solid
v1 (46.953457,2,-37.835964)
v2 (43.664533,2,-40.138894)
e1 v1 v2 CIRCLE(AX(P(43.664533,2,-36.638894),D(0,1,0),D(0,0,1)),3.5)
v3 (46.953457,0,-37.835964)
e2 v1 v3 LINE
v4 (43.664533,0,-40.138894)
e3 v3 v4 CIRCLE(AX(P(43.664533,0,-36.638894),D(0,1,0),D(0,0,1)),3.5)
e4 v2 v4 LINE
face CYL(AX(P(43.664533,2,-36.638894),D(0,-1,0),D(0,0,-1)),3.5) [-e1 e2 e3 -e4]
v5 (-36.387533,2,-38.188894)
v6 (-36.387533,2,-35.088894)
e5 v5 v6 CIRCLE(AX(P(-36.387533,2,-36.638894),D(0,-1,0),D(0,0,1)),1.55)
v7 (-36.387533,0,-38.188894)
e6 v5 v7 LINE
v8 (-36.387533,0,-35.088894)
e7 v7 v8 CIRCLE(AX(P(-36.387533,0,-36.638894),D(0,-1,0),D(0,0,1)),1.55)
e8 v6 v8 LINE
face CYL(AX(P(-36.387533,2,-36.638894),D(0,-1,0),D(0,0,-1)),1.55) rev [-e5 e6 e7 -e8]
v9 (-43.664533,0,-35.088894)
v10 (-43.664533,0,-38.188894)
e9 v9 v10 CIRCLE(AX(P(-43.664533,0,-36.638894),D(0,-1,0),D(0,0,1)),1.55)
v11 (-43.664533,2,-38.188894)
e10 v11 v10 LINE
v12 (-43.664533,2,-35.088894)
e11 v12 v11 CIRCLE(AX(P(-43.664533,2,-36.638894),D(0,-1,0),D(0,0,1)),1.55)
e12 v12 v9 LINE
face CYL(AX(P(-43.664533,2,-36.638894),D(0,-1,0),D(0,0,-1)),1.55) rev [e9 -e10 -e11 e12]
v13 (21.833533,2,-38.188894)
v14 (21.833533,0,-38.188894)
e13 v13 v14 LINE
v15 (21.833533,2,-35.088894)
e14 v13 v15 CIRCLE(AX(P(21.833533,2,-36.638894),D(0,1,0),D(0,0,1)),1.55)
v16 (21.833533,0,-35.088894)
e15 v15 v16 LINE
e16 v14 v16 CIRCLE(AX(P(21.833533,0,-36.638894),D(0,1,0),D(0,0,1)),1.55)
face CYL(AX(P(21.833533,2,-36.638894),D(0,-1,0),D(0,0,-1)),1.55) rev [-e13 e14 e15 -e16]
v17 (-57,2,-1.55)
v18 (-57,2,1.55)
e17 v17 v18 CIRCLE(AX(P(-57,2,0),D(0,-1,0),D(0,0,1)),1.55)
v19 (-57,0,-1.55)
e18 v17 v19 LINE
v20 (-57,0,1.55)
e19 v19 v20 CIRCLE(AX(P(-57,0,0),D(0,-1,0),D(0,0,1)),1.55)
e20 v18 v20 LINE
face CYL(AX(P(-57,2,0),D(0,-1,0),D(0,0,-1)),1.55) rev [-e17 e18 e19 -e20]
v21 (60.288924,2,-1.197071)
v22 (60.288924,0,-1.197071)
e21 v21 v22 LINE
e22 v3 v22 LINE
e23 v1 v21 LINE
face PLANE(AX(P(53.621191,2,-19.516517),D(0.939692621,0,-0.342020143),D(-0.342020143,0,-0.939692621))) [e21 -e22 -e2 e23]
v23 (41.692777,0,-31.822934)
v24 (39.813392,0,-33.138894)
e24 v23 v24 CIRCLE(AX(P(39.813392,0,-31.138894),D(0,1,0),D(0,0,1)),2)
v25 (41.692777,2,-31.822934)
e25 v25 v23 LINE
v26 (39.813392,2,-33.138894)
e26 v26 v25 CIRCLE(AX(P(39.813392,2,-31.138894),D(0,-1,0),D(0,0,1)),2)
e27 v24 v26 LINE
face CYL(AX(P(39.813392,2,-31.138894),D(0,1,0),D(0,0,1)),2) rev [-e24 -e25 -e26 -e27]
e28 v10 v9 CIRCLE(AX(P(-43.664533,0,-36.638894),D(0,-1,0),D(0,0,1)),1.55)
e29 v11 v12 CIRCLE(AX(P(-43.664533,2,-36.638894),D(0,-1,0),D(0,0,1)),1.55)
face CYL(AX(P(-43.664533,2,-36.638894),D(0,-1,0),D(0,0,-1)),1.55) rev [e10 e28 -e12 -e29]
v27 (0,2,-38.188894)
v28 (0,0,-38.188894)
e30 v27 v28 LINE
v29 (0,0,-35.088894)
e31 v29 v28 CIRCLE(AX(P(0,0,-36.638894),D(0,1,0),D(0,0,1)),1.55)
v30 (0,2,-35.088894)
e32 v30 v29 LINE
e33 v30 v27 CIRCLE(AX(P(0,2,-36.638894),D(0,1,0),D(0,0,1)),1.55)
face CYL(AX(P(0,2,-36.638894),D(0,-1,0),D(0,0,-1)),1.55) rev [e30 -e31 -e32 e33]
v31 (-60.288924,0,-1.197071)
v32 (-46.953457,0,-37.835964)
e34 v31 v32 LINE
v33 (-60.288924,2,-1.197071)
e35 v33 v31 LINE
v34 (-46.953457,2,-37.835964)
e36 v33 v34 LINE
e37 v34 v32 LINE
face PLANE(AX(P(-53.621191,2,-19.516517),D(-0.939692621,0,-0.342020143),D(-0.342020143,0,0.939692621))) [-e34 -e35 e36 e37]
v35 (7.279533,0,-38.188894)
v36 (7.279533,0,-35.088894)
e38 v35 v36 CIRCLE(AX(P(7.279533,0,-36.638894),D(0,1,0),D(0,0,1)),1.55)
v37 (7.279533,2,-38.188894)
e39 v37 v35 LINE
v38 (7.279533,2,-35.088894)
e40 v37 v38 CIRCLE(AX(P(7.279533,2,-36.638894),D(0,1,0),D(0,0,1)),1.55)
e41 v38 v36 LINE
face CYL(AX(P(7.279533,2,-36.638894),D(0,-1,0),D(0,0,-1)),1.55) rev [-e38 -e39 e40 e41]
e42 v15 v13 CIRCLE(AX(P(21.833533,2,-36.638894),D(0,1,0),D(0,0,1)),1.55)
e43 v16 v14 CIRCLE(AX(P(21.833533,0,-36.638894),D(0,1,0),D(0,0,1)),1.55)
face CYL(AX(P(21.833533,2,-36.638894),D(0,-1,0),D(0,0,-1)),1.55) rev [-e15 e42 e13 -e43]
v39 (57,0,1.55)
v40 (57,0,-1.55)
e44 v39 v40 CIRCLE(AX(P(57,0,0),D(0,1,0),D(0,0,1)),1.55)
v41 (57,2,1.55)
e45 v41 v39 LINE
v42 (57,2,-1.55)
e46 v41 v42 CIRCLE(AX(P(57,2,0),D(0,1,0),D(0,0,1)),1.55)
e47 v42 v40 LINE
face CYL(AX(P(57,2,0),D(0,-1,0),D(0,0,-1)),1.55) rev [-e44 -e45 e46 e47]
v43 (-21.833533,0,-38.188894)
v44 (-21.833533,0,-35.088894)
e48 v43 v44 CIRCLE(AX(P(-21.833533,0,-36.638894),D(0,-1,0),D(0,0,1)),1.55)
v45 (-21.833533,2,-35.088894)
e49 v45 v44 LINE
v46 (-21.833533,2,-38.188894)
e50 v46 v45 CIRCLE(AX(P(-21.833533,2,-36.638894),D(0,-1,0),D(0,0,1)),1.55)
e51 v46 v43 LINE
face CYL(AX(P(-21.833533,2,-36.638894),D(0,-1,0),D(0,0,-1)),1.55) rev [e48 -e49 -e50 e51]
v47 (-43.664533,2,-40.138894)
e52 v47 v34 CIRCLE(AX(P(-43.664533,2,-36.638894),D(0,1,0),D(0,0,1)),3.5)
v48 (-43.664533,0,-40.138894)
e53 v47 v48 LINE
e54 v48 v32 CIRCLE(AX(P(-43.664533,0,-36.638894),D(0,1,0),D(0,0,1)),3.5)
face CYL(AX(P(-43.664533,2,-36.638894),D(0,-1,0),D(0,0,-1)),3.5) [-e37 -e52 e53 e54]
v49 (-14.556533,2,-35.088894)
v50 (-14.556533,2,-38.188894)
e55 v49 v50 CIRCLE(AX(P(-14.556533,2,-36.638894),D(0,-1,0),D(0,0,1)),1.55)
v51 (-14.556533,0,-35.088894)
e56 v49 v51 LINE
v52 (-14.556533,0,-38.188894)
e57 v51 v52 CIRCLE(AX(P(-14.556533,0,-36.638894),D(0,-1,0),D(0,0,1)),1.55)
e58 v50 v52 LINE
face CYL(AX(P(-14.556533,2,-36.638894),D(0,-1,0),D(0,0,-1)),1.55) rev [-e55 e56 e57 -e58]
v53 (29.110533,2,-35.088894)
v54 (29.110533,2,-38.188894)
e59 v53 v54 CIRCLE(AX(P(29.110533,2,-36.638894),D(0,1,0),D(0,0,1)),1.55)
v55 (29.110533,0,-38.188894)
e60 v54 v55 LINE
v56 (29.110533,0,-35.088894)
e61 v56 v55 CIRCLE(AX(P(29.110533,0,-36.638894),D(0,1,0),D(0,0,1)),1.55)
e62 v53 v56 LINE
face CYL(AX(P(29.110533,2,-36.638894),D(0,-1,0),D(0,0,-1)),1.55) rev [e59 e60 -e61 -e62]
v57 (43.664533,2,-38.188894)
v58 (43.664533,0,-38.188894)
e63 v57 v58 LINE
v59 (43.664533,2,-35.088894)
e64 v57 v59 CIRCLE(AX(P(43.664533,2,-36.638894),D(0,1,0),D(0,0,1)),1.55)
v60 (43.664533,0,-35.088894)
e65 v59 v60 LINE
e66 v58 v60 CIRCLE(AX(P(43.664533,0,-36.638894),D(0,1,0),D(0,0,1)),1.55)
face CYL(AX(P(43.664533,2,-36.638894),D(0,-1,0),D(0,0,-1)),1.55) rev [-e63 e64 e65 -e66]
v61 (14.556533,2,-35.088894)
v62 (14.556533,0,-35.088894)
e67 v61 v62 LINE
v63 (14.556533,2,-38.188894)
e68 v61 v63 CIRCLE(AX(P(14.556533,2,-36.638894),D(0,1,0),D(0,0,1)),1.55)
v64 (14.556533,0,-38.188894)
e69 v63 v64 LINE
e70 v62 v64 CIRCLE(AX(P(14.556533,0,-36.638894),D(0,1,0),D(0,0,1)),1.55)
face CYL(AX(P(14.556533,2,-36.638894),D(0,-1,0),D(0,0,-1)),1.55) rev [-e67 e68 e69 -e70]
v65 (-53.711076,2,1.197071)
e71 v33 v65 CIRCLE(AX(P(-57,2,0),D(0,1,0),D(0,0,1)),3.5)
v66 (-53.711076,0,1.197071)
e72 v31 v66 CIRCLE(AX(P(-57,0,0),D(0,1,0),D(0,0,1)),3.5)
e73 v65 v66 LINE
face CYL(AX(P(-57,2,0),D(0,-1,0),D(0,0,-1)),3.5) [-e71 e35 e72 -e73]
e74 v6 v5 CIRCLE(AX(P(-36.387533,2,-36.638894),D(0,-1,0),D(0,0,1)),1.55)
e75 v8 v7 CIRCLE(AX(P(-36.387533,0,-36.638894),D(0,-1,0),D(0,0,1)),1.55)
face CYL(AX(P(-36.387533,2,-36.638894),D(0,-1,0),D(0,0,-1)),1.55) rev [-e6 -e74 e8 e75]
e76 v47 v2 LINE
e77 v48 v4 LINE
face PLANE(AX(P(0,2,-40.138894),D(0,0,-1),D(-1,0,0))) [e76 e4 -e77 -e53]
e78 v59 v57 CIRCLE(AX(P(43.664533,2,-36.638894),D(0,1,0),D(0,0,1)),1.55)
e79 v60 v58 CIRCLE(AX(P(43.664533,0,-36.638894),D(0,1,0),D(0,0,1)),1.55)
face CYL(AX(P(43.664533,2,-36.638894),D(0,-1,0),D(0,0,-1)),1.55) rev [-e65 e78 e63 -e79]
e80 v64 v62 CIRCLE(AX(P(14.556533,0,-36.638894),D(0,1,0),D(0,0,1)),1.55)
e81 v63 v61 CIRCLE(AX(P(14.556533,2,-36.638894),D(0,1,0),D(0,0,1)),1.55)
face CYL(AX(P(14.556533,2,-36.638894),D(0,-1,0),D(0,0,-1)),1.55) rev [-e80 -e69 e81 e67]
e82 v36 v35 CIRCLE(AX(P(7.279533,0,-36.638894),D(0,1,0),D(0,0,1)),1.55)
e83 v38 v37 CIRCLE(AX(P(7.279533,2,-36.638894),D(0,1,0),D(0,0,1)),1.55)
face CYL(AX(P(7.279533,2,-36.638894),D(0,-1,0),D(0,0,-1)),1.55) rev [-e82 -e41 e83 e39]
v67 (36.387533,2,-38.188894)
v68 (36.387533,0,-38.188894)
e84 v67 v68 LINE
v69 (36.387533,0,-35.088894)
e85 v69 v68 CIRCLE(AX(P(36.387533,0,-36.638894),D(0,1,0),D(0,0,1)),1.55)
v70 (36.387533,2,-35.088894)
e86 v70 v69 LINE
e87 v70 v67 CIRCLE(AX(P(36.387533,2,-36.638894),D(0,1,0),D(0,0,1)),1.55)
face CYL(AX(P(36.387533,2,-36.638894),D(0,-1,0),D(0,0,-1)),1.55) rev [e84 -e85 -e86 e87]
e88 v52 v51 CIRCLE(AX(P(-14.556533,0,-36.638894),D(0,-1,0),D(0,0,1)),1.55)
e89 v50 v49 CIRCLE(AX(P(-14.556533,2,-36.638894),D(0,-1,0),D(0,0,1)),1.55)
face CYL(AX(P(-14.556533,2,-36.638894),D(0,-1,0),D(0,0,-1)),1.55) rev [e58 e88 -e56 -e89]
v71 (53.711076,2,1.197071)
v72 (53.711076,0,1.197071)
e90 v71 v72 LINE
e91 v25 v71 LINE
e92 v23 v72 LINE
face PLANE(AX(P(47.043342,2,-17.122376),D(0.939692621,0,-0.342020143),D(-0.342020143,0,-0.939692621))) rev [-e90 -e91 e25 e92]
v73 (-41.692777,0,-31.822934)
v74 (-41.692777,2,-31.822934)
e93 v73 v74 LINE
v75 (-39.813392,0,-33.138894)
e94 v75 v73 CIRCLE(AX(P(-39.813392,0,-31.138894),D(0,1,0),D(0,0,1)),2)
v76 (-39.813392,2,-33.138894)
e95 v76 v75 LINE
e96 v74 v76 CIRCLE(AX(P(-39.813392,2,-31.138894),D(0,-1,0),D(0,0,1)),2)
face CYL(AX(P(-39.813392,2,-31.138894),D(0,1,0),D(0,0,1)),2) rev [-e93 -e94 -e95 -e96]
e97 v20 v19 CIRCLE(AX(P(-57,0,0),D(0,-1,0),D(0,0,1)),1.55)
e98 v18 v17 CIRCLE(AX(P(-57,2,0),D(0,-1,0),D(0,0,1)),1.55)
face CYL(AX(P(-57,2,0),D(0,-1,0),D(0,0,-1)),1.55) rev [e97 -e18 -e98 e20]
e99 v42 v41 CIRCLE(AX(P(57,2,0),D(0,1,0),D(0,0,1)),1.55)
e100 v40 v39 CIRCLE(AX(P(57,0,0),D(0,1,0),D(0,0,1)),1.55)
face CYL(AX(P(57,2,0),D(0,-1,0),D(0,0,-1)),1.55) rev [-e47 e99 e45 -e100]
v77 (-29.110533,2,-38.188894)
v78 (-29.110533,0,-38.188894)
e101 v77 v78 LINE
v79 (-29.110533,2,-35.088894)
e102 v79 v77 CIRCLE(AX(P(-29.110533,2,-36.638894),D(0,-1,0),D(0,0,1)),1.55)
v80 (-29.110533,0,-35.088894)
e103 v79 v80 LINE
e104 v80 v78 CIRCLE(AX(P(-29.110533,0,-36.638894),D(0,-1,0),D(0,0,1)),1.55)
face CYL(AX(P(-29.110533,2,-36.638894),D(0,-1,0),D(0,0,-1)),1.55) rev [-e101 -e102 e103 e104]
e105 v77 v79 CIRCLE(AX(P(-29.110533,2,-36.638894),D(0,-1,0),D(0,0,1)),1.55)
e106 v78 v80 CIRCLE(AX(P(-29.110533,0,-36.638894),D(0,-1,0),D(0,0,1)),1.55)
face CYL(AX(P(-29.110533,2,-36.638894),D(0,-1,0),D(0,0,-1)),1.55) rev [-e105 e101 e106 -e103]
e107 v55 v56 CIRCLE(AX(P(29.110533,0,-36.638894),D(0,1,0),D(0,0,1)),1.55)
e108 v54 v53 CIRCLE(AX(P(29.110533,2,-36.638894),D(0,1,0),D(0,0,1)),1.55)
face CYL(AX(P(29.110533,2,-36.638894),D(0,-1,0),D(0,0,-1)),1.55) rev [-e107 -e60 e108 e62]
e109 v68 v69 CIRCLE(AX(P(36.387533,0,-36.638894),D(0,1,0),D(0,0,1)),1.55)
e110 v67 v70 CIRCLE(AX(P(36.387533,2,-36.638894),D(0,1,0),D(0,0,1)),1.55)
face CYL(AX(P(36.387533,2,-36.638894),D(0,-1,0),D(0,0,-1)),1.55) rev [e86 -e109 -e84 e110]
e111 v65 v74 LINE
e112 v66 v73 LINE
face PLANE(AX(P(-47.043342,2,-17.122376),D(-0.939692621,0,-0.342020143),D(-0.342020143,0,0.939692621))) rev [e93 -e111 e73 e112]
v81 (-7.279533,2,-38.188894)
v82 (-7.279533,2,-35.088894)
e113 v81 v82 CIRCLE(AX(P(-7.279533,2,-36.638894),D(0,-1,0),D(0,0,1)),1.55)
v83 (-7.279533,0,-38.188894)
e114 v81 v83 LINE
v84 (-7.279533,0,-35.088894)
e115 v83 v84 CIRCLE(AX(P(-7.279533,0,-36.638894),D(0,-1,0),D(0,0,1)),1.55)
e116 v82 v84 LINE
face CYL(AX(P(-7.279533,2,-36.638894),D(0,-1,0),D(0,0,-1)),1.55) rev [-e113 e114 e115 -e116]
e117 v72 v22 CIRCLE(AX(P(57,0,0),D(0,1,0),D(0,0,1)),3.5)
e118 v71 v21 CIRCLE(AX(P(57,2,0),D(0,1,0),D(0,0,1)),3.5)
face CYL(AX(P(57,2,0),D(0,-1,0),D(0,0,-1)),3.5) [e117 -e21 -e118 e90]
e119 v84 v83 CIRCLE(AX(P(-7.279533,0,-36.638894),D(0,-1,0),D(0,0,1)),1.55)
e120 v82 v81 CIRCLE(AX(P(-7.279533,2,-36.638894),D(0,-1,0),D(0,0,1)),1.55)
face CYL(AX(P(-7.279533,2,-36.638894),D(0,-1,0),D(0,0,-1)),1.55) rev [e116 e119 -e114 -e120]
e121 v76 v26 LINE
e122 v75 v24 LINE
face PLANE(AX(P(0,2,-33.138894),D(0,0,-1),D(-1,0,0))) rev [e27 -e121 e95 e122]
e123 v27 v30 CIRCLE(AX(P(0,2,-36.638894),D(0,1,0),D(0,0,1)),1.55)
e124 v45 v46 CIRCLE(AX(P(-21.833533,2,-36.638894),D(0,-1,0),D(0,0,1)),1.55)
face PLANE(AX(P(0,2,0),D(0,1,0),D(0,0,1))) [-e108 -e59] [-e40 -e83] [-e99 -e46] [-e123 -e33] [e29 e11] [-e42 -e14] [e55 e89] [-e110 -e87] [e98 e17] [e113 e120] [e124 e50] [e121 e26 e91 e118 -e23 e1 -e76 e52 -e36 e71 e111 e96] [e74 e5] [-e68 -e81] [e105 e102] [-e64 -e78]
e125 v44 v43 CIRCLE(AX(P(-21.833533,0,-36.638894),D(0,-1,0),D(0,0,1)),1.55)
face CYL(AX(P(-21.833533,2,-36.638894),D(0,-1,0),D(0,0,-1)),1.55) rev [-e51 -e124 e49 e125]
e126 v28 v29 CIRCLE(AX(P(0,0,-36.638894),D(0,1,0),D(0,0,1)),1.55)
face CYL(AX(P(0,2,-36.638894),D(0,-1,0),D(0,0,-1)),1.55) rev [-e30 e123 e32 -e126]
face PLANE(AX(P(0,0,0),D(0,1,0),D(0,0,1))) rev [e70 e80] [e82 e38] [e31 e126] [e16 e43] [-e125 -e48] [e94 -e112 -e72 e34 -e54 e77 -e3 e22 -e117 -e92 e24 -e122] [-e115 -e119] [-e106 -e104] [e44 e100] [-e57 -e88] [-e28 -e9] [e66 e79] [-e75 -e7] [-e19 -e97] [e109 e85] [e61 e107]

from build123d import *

# Parameters (mm, degrees)
SKETCH_1_R      = 1.55
EXTRUDE_1_DEPTH = 2
FILLET_1_R      = 2


with BuildPart() as part:
    # 草图1 → 凸台-拉伸1 (new body)
    with BuildSketch(Plane(origin=(0, 0, 0), x_dir=(1, 0, 0), z_dir=(0, 1, 0))):
        with BuildLine():
            Line((41.213806874, 33.138893752), (53.711075827, -1.197070502))
            ThreePointArc((53.711075827, -1.197070502), (58.197070502, -3.288924173), (60.288924173, 1.197070502))
            Line((60.288924173, 1.197070502), (46.953457431, 37.835964254))
            ThreePointArc((46.953457431, 37.835964254), (45.672050785, 39.505925907), (43.664533258, 40.138893752))
            Line((43.664533258, 40.138893752), (-43.664533258, 40.138893752))
            ThreePointArc((-43.664533258, 40.138893752), (-45.672050785, 39.505925907), (-46.953457431, 37.835964254))
            Line((-46.953457431, 37.835964254), (-60.288924173, 1.197070502))
            ThreePointArc((-60.288924173, 1.197070502), (-58.197070502, -3.288924173), (-53.711075827, -1.197070502))
            Line((-53.711075827, -1.197070502), (-41.213806874, 33.138893752))
            Line((-41.213806874, 33.138893752), (41.213806874, 33.138893752))
        make_face()
        with Locations(Location((43.664533258, 36.638893752, 0), (0, 0, 270))):
            Circle(SKETCH_1_R, mode=Mode.SUBTRACT)
        with Locations(Location((57, 0, 0), (0, 0, 270))):
            Circle(SKETCH_1_R, mode=Mode.SUBTRACT)
        with Locations(Location((29.110533258, 36.638893752, 0), (0, 0, 270))):
            Circle(SKETCH_1_R, mode=Mode.SUBTRACT)
        with Locations(Location((36.387533258, 36.638893752, 0), (0, 0, 270))):
            Circle(SKETCH_1_R, mode=Mode.SUBTRACT)
        with Locations(Location((-36.387533258, 36.638893752, 0), (0, 0, 270))):
            Circle(SKETCH_1_R, mode=Mode.SUBTRACT)
        with Locations(Location((-29.110533258, 36.638893752, 0), (0, 0, 270))):
            Circle(SKETCH_1_R, mode=Mode.SUBTRACT)
        with Locations(Location((-21.833533258, 36.638893752, 0), (0, 0, 270))):
            Circle(SKETCH_1_R, mode=Mode.SUBTRACT)
        with Locations(Location((-14.556533258, 36.638893752, 0), (0, 0, 270))):
            Circle(SKETCH_1_R, mode=Mode.SUBTRACT)
        with Locations(Location((-7.279533258, 36.638893752, 0), (0, 0, 270))):
            Circle(SKETCH_1_R, mode=Mode.SUBTRACT)
        with Locations(Location((0, 36.638893752, 0), (0, 0, 270))):
            Circle(SKETCH_1_R, mode=Mode.SUBTRACT)
        with Locations(Location((7.279533258, 36.638893752, 0), (0, 0, 270))):
            Circle(SKETCH_1_R, mode=Mode.SUBTRACT)
        with Locations(Location((14.556533258, 36.638893752, 0), (0, 0, 270))):
            Circle(SKETCH_1_R, mode=Mode.SUBTRACT)
        with Locations(Location((21.833533258, 36.638893752, 0), (0, 0, 270))):
            Circle(SKETCH_1_R, mode=Mode.SUBTRACT)
        with Locations(Location((-43.664533258, 36.638893752, 0), (0, 0, 270))):
            Circle(SKETCH_1_R, mode=Mode.SUBTRACT)
        with Locations(Location((-57, 0, 0), (0, 0, 270))):
            Circle(SKETCH_1_R, mode=Mode.SUBTRACT)
    extrude(amount=EXTRUDE_1_DEPTH)

    # 圆角1
    fillet_1_edges = [part.edges().sort_by_distance(p)[0] for p in [
        (-41.213806874, 1, -33.138893752),
        (41.213806874, 1, -33.138893752),
    ]]
    fillet(fillet_1_edges, radius=FILLET_1_R)


solid = part.part
